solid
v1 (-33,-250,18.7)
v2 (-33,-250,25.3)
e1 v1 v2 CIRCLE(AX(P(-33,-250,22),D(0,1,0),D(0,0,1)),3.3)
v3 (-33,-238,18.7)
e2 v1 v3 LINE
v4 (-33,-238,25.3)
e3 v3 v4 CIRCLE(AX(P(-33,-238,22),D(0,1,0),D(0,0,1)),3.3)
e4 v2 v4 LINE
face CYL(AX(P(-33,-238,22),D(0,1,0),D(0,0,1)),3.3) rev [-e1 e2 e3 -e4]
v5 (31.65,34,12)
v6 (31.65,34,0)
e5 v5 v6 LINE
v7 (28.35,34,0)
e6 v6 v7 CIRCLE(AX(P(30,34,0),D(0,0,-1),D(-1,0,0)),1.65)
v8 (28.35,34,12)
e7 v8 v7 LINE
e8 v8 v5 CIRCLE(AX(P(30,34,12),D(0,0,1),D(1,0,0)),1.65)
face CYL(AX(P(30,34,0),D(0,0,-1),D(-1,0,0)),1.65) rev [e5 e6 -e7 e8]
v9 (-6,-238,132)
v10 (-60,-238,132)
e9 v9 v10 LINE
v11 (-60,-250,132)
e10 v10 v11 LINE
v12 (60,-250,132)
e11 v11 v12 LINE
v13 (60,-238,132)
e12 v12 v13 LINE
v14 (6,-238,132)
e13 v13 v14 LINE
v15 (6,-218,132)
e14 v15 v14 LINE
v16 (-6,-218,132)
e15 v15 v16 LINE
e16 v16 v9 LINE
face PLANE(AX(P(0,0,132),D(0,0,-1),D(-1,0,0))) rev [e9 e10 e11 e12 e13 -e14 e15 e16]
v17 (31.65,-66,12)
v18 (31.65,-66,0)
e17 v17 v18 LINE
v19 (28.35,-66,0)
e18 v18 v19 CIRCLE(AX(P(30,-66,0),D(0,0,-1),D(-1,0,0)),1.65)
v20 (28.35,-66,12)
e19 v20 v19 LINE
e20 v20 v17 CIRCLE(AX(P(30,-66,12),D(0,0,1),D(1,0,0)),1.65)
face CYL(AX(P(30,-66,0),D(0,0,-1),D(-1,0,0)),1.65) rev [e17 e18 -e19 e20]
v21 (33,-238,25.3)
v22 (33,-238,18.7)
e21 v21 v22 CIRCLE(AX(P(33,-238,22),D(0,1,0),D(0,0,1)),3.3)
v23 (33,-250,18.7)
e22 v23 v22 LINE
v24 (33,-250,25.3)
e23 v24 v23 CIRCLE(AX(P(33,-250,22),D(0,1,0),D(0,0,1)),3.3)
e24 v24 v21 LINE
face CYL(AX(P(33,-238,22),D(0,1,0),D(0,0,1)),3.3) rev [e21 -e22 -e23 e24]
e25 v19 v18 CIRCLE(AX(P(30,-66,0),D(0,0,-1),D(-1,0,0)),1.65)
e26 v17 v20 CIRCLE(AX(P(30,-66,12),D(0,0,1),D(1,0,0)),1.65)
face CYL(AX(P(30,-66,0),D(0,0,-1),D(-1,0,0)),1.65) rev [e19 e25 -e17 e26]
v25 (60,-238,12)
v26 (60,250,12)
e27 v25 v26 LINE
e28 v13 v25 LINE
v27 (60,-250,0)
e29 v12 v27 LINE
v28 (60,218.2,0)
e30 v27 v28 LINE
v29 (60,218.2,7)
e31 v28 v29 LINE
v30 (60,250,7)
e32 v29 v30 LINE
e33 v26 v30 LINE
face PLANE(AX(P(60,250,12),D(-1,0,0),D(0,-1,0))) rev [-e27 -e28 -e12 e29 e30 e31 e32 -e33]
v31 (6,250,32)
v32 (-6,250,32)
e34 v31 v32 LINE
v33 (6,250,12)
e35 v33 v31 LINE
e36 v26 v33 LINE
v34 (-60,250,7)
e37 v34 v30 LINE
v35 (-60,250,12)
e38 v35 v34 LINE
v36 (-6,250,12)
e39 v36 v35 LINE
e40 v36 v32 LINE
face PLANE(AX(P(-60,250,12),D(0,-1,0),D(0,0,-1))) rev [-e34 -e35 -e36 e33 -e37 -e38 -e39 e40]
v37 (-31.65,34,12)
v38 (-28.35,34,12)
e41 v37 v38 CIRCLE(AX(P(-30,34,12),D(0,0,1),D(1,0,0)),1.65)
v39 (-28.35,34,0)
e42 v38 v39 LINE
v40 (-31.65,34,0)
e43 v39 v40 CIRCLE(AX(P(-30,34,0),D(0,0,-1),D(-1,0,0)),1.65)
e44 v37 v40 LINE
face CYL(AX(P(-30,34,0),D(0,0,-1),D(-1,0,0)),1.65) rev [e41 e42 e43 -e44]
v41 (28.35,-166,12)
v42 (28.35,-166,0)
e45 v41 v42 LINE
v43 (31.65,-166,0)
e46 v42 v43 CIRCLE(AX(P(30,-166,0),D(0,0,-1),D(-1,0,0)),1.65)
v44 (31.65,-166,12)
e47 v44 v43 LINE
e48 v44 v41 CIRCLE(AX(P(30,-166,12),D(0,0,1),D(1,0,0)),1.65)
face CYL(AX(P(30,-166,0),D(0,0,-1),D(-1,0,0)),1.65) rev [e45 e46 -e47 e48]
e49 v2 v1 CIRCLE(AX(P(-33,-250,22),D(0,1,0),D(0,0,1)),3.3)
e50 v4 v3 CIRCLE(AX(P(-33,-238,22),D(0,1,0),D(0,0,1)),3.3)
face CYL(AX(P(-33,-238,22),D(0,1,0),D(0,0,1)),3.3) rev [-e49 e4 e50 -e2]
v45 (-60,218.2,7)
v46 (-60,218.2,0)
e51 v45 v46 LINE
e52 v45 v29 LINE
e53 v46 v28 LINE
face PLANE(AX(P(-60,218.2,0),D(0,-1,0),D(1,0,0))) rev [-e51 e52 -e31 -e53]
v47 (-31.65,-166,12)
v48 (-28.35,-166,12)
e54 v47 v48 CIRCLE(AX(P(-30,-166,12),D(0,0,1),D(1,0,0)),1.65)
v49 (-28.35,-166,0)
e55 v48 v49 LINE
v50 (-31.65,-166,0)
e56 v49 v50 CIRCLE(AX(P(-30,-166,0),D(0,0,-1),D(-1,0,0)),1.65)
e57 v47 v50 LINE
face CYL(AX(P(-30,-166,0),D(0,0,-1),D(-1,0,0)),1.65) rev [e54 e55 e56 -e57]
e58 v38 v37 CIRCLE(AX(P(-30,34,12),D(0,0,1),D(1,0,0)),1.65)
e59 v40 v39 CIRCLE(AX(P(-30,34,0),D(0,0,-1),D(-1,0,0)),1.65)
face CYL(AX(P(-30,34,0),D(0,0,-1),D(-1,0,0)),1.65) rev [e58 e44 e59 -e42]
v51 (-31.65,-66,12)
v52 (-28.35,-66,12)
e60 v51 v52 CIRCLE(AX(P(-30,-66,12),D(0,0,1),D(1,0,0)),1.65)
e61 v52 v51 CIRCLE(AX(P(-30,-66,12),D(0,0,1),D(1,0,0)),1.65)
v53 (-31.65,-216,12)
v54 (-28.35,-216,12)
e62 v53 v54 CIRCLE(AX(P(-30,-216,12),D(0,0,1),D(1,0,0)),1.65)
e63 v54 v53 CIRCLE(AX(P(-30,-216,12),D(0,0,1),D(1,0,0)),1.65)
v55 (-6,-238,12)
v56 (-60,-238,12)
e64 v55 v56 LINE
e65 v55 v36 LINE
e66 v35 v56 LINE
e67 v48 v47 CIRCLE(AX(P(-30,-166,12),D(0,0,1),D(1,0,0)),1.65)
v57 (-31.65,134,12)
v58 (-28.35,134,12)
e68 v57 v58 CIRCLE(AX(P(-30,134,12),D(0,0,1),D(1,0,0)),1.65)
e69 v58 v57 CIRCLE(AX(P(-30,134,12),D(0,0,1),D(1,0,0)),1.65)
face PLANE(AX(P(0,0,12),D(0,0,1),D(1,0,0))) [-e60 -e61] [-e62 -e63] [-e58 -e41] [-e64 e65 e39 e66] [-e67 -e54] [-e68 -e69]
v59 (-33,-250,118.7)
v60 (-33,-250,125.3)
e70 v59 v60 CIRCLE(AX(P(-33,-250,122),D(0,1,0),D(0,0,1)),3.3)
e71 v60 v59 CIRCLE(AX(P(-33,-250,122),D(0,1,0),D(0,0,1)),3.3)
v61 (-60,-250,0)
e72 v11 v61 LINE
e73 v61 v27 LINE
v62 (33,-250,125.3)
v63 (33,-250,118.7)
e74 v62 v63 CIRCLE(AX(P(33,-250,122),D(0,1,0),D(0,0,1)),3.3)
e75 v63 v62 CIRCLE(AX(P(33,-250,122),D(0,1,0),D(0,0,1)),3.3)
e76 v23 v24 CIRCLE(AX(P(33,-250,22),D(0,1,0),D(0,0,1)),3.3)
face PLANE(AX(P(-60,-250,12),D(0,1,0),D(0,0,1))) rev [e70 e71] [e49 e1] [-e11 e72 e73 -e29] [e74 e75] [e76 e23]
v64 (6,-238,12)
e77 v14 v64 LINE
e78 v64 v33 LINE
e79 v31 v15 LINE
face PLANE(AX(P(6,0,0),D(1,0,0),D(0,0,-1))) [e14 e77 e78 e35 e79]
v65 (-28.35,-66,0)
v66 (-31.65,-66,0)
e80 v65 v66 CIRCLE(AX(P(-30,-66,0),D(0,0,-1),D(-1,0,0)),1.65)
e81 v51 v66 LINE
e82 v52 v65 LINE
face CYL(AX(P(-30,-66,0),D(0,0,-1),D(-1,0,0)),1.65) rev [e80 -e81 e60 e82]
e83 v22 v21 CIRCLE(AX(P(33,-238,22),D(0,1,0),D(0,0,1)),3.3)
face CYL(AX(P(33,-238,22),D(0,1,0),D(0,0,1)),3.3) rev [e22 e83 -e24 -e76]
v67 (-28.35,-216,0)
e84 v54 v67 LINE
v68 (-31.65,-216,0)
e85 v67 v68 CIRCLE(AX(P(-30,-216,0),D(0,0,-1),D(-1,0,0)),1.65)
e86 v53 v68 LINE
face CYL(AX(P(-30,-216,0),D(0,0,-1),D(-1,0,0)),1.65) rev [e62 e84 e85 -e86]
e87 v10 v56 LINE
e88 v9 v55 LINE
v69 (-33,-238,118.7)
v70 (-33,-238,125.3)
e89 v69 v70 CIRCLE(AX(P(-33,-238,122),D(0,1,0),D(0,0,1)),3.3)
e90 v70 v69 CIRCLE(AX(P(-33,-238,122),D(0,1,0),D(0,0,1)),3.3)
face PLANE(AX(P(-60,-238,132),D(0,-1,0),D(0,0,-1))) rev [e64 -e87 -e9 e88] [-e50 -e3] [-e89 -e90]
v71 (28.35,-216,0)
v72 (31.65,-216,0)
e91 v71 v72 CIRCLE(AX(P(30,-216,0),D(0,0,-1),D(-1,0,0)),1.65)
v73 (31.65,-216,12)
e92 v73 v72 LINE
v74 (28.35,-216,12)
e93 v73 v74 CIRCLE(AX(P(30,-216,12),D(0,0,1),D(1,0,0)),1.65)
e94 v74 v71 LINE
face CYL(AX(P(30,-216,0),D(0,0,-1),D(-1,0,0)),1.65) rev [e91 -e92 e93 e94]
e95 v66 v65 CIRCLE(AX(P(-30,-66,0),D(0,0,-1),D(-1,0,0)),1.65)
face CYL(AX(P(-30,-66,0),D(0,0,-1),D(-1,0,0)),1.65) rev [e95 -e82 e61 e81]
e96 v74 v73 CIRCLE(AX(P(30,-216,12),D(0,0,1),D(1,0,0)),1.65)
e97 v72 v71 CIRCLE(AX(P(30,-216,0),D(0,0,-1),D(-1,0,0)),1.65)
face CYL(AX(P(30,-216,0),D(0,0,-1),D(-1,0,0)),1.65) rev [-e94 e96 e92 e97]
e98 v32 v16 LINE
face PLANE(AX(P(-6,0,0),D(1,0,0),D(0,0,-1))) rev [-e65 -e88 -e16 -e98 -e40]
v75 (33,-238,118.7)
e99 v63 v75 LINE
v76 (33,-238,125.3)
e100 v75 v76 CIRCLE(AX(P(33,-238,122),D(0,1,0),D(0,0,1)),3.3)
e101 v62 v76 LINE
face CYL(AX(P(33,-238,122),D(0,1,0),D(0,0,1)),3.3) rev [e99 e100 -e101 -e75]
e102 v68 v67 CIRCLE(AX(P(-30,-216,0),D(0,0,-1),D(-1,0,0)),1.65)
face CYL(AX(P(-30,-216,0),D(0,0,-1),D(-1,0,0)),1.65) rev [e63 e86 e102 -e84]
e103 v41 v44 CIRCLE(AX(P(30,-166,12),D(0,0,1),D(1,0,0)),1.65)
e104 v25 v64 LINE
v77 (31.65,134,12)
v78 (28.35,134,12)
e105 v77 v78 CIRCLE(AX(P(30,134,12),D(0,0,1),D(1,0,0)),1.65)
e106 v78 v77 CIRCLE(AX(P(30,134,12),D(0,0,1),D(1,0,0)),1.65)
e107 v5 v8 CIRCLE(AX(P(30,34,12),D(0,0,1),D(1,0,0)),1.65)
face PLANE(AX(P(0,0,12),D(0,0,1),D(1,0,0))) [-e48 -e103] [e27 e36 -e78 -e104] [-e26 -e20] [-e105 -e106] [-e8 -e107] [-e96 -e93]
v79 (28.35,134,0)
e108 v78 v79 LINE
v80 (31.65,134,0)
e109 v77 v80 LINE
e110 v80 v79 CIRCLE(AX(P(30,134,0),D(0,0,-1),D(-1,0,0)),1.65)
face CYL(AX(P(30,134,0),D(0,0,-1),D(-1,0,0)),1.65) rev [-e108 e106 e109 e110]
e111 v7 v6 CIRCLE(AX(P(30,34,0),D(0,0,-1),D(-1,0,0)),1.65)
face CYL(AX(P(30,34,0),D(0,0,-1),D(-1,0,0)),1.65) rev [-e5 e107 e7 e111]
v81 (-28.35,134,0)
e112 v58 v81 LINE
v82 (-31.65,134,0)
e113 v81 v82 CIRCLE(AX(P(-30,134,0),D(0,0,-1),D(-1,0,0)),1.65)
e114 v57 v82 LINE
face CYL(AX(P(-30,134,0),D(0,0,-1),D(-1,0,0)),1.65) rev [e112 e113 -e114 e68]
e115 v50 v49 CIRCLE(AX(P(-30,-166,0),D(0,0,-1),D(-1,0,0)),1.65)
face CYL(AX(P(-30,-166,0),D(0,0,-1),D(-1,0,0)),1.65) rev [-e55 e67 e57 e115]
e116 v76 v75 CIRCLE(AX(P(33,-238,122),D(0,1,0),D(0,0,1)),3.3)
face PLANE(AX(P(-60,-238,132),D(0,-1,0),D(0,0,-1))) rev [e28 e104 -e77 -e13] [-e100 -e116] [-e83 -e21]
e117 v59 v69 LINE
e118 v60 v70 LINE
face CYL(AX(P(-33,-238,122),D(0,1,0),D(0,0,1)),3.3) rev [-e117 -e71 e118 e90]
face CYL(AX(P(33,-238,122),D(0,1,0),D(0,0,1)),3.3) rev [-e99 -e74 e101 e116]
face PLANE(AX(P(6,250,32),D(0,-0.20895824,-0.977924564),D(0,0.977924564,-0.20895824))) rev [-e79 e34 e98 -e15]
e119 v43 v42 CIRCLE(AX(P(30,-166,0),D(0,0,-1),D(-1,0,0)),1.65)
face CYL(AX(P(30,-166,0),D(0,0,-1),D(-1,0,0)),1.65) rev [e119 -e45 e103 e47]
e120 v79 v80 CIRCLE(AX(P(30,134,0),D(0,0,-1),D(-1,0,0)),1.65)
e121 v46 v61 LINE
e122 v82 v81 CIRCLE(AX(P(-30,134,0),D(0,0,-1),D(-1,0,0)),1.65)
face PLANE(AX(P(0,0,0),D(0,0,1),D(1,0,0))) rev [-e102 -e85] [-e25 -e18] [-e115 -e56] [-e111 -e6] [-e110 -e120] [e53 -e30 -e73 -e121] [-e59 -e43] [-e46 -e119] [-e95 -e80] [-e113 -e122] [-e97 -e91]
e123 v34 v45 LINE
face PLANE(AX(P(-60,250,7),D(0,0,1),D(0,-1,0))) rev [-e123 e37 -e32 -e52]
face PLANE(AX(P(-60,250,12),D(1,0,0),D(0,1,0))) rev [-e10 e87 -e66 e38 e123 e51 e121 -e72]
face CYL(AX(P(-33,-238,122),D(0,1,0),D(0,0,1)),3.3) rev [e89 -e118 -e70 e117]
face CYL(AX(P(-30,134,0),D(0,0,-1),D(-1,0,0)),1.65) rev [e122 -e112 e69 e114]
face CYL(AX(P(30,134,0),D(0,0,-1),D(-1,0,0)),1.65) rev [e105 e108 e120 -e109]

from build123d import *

# Parameters (mm, degrees)
SKETCH1_W                = 120
SKETCH1_H                = 500
BOSS_EXTRUDE1_DEPTH      = 12
SKETCH2_W                = 120
SKETCH2_H                = 12
BOSS_EXTRUDE2_DEPTH      = 120
BOSS_EXTRUDE3_DEPTH      = 6
M6_CLEARANCE_HOLE1_D     = 6.6
M6_CLEARANCE_HOLE1_DEPTH = 15
M6_CLEARANCE_HOLE1_TIP   = 1.982840043
M6_CLEARANCE_HOLE2_D     = 6.6
M6_CLEARANCE_HOLE2_DEPTH = 15
M6_CLEARANCE_HOLE2_TIP   = 1.982840043
M4_TAPPED_HOLE1_D        = 3.3
CUT_EXTRUDE1_DEPTH       = 308.122125546
CUT_EXTRUDE1_DEPTH_BACK  = 308.122125546
SKETCH10_W               = 7
SKETCH10_H               = 31.8


with BuildPart() as part:
    # Sketch1 → Boss-Extrude1 (new body)
    with BuildSketch(Plane.XY):
        Rectangle(SKETCH1_W, SKETCH1_H)
    extrude(amount=BOSS_EXTRUDE1_DEPTH)

    # Sketch2 → Boss-Extrude2 (add)
    with BuildSketch(Plane.XY.offset(12)):
        with Locations((0, -244)):
            Rectangle(SKETCH2_W, SKETCH2_H)
    extrude(amount=BOSS_EXTRUDE2_DEPTH)

    # Sketch3 → Boss-Extrude3 (add, symmetric)
    with BuildSketch(Plane(origin=(0, 0, 0), x_dir=(0, 0, -1), z_dir=(1, 0, 0))):
        Polygon((-12, 250), (-32, 250), (-132, -218), (-132, -238), (-12, -238), align=None)
    extrude(amount=BOSS_EXTRUDE3_DEPTH, both=True)

    # M6 Clearance Hole1
    with Locations(Plane(origin=(0, -238, 0), x_dir=(1, 0, 0), z_dir=(0, 1, 0))):
        with Locations((33, -122), (33, -22)):
            Hole(M6_CLEARANCE_HOLE1_D / 2, depth=M6_CLEARANCE_HOLE1_DEPTH)
            with Locations((0, 0, -(M6_CLEARANCE_HOLE1_DEPTH + M6_CLEARANCE_HOLE1_TIP / 2))):  # 118° drill point
                Cone(0, M6_CLEARANCE_HOLE1_D / 2, M6_CLEARANCE_HOLE1_TIP, mode=Mode.SUBTRACT)

    # M6 Clearance Hole2
    with Locations(Plane(origin=(0, -238, 0), x_dir=(1, 0, 0), z_dir=(0, 1, 0))):
        with Locations((-33, -122), (-33, -22)):
            Hole(M6_CLEARANCE_HOLE2_D / 2, depth=M6_CLEARANCE_HOLE2_DEPTH)
            with Locations((0, 0, -(M6_CLEARANCE_HOLE2_DEPTH + M6_CLEARANCE_HOLE2_TIP / 2))):  # 118° drill point
                Cone(0, M6_CLEARANCE_HOLE2_D / 2, M6_CLEARANCE_HOLE2_TIP, mode=Mode.SUBTRACT)

    # M4 Tapped Hole1 (through all)
    with Locations(Plane(origin=(0, 0, 0), x_dir=(-1, 0, 0), z_dir=(0, 0, -1))):
        with Locations((-30, 34), (-30, 134), (-30, -66), (-30, -166), (-30, -216), (30, -216), (30, -166), (30, -66), (30, 34), (30, 134)):
            Hole(M4_TAPPED_HOLE1_D / 2)

    # Sketch10 → Cut-Extrude1 (cut, two sides: drawn at the far end of the back side and taken through both)
    with BuildSketch(Plane(origin=(60, 0, 0), x_dir=(0, 0, -1), z_dir=(1, 0, 0)).offset(-CUT_EXTRUDE1_DEPTH_BACK)):
        with Locations((-3.5, 234.1)):
            Rectangle(SKETCH10_W, SKETCH10_H)
    extrude(amount=CUT_EXTRUDE1_DEPTH + CUT_EXTRUDE1_DEPTH_BACK, mode=Mode.SUBTRACT)


solid = part.part
